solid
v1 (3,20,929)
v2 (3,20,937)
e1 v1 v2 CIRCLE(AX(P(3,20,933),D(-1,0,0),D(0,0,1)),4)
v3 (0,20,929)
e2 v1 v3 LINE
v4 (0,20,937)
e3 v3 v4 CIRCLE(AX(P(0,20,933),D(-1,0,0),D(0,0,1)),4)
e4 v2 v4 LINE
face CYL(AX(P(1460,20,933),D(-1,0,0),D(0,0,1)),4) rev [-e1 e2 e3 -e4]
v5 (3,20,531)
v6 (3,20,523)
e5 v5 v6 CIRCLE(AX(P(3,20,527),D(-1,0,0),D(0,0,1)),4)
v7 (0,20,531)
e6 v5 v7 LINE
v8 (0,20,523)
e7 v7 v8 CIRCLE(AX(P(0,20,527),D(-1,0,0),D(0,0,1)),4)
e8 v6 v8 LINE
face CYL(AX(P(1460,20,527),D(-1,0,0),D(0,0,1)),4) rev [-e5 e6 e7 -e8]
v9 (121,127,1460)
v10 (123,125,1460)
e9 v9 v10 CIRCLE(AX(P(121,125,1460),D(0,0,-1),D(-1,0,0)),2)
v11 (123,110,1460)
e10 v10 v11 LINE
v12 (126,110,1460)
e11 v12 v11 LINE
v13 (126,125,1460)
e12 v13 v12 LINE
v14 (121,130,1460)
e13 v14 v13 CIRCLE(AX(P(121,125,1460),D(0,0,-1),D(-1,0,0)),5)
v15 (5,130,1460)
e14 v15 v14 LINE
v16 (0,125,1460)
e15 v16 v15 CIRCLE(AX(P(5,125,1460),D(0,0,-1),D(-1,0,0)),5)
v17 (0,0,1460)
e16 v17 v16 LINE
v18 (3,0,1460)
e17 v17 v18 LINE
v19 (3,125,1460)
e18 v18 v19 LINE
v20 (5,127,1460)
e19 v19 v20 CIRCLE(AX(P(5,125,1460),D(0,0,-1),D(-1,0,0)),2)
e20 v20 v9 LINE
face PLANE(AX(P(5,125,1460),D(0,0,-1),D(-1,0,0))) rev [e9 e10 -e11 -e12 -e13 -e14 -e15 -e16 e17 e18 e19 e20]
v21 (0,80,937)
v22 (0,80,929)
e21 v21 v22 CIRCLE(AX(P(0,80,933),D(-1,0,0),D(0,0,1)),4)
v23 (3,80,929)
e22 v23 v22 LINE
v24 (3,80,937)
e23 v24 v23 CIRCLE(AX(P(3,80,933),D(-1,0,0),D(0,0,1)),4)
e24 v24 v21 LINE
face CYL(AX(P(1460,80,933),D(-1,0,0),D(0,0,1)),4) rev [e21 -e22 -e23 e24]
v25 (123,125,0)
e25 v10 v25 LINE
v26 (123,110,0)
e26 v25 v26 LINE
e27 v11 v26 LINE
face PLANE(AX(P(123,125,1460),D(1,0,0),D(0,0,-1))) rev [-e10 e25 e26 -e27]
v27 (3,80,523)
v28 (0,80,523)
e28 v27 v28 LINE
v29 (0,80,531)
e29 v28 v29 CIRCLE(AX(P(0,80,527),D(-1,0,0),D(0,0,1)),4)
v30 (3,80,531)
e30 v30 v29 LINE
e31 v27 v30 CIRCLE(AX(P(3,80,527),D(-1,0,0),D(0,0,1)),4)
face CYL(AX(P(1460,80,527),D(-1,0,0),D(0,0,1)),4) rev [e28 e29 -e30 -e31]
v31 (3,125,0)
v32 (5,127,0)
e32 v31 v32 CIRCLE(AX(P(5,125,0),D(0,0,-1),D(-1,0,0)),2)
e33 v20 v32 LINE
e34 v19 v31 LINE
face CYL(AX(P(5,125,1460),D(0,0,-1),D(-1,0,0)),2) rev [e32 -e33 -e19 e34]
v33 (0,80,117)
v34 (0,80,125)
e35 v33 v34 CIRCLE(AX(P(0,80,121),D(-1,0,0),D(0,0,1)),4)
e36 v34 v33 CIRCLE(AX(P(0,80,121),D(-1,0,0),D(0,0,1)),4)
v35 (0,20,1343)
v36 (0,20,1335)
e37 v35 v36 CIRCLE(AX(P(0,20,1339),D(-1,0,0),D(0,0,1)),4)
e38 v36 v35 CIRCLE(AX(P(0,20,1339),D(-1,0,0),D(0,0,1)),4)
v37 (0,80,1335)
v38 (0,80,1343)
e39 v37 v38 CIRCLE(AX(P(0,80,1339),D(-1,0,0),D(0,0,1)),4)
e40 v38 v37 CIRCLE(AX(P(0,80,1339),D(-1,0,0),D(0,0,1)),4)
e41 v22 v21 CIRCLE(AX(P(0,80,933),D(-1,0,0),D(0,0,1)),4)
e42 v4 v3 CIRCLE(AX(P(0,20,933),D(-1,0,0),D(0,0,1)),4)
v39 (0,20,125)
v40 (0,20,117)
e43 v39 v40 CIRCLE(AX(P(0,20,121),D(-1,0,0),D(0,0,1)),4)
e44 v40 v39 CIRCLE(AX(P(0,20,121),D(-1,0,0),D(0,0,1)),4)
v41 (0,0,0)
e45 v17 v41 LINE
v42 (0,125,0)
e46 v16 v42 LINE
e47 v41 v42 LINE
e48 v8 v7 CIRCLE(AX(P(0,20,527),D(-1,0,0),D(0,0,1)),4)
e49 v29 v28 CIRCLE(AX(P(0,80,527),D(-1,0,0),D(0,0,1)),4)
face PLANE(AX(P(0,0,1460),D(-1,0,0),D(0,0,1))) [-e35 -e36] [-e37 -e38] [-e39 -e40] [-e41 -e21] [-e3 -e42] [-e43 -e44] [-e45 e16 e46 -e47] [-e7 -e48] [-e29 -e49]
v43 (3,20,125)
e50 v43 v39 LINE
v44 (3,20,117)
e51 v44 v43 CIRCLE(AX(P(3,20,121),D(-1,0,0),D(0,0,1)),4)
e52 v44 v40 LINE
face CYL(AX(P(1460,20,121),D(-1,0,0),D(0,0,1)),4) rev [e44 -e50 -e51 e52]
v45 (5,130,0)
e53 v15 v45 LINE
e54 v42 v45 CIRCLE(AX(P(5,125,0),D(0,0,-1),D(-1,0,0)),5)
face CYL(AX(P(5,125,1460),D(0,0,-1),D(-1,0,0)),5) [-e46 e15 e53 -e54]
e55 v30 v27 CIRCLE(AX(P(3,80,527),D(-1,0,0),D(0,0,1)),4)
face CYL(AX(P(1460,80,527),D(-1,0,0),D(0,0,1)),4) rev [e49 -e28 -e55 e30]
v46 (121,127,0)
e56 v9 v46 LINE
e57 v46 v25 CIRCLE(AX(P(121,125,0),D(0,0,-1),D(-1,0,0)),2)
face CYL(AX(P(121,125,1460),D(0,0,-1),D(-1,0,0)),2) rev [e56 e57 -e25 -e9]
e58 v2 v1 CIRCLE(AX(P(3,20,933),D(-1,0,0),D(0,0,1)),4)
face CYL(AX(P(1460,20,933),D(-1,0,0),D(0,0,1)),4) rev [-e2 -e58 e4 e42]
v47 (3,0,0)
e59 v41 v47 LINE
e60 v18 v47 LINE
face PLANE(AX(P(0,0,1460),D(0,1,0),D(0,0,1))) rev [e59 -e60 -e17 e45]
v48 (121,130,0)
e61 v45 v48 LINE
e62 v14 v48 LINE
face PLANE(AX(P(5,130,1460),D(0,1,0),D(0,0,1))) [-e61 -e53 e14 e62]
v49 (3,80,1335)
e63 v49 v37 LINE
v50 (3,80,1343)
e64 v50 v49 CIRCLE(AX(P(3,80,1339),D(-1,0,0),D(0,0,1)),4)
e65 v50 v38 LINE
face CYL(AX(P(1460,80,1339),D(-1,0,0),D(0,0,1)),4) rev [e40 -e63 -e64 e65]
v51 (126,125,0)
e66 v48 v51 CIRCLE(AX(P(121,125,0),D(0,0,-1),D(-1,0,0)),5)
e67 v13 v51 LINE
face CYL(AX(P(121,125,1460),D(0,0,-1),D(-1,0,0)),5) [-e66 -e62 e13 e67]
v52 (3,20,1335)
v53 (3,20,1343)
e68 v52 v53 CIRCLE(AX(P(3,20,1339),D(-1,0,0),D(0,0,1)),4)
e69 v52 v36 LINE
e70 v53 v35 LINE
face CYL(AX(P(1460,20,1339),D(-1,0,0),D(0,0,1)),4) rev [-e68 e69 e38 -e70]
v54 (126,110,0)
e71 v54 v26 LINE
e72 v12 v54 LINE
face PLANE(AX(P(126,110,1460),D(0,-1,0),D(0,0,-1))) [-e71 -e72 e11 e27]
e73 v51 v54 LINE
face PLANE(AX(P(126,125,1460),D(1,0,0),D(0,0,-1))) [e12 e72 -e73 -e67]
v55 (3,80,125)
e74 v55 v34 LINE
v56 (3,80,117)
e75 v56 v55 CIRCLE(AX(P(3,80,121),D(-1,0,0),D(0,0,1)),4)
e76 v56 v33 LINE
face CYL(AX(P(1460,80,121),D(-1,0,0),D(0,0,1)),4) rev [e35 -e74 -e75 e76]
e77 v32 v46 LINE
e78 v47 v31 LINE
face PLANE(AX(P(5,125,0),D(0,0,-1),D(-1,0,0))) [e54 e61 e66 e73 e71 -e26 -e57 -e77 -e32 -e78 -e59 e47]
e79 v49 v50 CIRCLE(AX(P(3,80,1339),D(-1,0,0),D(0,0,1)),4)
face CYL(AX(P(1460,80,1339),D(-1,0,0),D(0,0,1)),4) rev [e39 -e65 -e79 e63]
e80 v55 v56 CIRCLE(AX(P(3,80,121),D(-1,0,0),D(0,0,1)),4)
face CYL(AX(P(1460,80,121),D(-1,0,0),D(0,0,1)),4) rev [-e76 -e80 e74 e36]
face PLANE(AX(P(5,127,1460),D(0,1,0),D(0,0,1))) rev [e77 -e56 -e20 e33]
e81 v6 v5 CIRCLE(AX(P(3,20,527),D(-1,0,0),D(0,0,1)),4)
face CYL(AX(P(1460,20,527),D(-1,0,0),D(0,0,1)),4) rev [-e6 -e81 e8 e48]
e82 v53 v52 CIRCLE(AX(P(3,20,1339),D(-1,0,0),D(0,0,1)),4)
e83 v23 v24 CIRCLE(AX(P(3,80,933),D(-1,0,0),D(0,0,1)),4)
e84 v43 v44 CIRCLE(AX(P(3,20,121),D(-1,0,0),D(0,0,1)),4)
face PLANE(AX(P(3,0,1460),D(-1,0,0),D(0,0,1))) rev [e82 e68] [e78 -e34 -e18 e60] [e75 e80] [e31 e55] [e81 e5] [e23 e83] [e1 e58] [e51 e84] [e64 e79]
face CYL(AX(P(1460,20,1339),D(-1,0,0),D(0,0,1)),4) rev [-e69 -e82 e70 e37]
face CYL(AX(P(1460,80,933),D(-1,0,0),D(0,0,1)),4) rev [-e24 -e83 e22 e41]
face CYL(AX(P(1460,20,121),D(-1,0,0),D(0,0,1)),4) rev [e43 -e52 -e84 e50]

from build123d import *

# Parameters (mm, degrees)
BOSS_EXTRUDE1_DEPTH = 1460
SKETCH2_R           = 4
CUT_EXTRUDE1_DEPTH  = 1460


with BuildPart() as part:
    # Sketch1 → Boss-Extrude1 (new body)
    with BuildSketch(Plane.XY):
        with BuildLine():
            Line((0, 0), (0, 125))
            ThreePointArc((0, 125), (1.464466094, 128.535533906), (5, 130))
            Line((5, 130), (121, 130))
            ThreePointArc((121, 130), (124.535533906, 128.535533906), (126, 125))
            Line((126, 125), (126, 110))
            Line((126, 110), (123, 110))
            Line((123, 110), (123, 125))
            ThreePointArc((123, 125), (122.414213562, 126.414213562), (121, 127))
            Line((121, 127), (5, 127))
            ThreePointArc((5, 127), (3.585786438, 126.414213562), (3, 125))
            Line((3, 125), (3, 0))
            Line((3, 0), (0, 0))
        make_face()
    extrude(amount=BOSS_EXTRUDE1_DEPTH)

    # Sketch2 → Cut-Extrude1 (cut)
    with BuildSketch(Plane.ZY):
        with Locations((121, 80)):
            Circle(SKETCH2_R)
        with Locations((1339, 80)):
            Circle(SKETCH2_R)
        with Locations((933, 80)):
            Circle(SKETCH2_R)
        with Locations((527, 80)):
            Circle(SKETCH2_R)
        with Locations((121, 20)):
            Circle(SKETCH2_R)
        with Locations((1339, 20)):
            Circle(SKETCH2_R)
        with Locations((933, 20)):
            Circle(SKETCH2_R)
        with Locations((527, 20)):
            Circle(SKETCH2_R)
    extrude(amount=-CUT_EXTRUDE1_DEPTH, mode=Mode.SUBTRACT)


solid = part.part
